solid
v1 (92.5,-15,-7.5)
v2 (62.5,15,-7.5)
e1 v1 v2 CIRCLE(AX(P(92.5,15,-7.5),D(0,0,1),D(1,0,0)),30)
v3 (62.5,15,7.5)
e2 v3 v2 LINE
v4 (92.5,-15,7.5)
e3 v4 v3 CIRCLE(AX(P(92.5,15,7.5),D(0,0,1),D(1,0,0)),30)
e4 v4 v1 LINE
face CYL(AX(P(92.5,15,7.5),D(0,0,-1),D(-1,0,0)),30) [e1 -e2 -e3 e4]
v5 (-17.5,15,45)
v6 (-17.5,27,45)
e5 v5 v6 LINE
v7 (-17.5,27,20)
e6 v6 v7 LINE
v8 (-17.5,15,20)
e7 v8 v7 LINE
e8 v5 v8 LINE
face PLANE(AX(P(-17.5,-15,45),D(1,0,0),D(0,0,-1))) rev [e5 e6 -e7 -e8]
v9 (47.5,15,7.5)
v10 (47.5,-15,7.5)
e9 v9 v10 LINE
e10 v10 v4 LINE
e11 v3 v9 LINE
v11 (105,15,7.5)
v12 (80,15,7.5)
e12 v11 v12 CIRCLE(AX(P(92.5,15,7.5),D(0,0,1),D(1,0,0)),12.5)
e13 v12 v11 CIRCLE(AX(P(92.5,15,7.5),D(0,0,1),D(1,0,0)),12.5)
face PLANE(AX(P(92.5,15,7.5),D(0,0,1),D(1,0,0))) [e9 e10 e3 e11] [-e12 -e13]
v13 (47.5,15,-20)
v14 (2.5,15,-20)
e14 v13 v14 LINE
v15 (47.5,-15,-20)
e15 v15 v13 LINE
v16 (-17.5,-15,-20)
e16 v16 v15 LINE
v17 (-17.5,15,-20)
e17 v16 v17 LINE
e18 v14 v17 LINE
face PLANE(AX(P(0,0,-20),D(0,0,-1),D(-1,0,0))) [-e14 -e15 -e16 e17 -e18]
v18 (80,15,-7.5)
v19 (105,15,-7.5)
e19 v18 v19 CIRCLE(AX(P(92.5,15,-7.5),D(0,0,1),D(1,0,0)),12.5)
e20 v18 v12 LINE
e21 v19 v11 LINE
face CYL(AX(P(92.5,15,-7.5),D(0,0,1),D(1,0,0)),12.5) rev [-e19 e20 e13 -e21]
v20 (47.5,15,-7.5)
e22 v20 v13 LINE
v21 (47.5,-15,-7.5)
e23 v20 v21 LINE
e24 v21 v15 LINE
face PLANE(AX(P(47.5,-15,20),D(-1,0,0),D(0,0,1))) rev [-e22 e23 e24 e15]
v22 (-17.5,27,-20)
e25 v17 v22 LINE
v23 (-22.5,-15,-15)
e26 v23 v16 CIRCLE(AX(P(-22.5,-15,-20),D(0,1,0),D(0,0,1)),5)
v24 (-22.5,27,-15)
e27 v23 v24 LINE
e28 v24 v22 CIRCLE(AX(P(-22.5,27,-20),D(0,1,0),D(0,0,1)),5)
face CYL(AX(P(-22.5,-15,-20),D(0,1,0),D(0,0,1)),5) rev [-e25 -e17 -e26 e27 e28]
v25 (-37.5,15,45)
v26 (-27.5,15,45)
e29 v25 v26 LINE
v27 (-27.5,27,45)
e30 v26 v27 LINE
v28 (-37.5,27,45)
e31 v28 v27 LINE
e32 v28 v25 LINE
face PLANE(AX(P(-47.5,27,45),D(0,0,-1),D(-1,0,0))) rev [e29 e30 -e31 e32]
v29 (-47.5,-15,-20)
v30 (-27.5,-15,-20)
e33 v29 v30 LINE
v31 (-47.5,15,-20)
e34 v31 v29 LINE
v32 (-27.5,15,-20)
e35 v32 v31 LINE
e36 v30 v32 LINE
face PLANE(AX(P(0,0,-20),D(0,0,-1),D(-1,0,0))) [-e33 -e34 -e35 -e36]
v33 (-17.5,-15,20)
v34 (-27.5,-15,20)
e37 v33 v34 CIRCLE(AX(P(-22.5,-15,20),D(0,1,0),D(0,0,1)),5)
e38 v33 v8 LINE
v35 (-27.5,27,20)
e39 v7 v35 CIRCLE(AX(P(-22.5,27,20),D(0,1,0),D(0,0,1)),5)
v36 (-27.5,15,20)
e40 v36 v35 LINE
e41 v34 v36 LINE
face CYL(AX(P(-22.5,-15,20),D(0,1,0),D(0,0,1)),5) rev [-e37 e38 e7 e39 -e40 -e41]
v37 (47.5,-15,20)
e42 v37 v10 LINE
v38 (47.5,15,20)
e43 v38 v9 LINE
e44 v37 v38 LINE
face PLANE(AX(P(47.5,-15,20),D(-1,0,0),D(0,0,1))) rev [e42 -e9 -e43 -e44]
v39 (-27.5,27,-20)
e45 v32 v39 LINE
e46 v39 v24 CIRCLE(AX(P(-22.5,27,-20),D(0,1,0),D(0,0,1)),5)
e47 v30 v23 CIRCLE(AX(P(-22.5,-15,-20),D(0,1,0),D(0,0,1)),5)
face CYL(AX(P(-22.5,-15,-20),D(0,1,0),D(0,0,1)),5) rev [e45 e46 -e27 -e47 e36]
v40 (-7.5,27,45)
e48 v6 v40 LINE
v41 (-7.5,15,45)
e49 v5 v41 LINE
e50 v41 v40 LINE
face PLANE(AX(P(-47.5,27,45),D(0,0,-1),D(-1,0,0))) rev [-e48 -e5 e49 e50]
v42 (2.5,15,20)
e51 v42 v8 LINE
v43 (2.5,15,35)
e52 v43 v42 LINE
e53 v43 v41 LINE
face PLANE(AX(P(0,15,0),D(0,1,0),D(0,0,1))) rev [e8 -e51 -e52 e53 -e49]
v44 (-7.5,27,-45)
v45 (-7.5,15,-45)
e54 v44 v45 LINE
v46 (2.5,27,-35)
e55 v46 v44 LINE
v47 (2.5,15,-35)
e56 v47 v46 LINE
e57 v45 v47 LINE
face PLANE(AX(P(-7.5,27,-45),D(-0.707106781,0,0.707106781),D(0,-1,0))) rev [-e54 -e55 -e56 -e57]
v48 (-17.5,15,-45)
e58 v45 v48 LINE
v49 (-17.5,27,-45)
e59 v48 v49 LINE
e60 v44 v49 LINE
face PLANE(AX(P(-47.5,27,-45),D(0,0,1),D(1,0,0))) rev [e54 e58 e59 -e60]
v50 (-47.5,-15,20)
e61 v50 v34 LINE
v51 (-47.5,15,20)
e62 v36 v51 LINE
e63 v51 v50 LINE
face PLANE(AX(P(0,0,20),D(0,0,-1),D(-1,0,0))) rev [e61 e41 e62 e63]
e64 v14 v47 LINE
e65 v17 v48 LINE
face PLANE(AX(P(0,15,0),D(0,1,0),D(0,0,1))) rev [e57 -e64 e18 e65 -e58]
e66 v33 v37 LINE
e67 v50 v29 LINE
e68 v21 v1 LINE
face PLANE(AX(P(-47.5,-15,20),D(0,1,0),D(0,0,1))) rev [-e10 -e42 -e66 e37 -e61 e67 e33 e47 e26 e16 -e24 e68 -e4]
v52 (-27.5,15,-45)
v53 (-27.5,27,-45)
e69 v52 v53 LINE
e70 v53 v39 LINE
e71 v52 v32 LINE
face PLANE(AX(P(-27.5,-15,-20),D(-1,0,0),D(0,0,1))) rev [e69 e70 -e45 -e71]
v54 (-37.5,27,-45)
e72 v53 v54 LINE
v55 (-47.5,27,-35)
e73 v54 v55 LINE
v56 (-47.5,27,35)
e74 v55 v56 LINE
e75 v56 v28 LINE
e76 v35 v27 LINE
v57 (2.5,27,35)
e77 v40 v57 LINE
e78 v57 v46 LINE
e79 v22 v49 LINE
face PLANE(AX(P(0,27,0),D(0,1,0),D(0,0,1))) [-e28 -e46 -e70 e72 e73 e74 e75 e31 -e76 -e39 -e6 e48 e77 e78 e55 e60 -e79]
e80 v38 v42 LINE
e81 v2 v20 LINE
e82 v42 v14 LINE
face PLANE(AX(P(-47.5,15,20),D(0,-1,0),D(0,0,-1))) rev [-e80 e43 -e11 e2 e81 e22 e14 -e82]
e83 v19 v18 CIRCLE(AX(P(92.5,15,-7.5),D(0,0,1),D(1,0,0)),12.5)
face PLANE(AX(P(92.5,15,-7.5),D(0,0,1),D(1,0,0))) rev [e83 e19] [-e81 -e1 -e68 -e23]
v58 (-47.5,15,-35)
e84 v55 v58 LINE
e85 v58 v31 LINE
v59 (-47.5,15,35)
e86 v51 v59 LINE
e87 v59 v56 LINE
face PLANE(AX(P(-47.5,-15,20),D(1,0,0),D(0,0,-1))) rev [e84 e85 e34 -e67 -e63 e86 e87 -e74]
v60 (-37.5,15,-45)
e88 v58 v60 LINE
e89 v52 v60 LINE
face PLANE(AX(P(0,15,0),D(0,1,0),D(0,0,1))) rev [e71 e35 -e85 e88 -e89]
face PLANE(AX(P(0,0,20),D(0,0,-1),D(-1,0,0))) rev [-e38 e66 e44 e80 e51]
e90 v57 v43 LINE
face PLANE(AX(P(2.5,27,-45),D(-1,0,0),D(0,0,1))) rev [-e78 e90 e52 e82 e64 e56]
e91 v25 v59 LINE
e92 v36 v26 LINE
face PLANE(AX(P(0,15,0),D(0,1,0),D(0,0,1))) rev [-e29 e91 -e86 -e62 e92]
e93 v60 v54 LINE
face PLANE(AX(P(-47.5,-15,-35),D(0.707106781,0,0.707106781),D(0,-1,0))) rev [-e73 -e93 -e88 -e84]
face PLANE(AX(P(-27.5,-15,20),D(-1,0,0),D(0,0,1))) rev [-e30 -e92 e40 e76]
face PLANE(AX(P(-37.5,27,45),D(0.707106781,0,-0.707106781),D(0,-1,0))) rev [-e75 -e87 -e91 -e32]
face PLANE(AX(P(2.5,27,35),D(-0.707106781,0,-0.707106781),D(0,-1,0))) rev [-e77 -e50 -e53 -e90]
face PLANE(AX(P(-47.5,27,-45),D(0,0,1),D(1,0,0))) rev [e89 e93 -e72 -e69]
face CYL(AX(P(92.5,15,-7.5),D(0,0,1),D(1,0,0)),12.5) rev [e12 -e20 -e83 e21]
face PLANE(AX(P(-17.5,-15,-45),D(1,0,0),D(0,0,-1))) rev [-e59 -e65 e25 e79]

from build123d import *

# Parameters (mm, degrees)
ROD_BODY_SKETCH_W                = 95
ROD_BODY_SKETCH_H                = 30
ROD_BODY_30X95_DEPTH             = 20
MOUNTING_PLATE_SKETCH_W          = 50
MOUNTING_PLATE_SKETCH_H          = 90
MOUNTING_PLATE_12MM_DEPTH        = 12
EYE_BOSS_DEPTH                   = 7.5
EYE_HOLE_SKETCH_R                = 12.5
EYE_HOLE_25_DEPTH                = 15
MOUNTING_SLOTS_2X10_DEPTH        = 138.095769446
PLATE_CORNER_CHAMFERS_10X45_SIZE = 10


with BuildPart() as part:
    # Rod Body Sketch → Rod Body 30x95 (new, symmetric)
    with BuildSketch(Plane.XY):
        Rectangle(ROD_BODY_SKETCH_W, ROD_BODY_SKETCH_H)
    extrude(amount=ROD_BODY_30X95_DEPTH, both=True)

    # Mounting Plate Sketch → Mounting Plate 12mm (add)
    with BuildSketch(Plane(origin=(0, 15, 0), x_dir=(1, 0, 0), z_dir=(0, 1, 0))):
        with Locations((-22.5, 0)):
            Rectangle(MOUNTING_PLATE_SKETCH_W, MOUNTING_PLATE_SKETCH_H)
    extrude(amount=MOUNTING_PLATE_12MM_DEPTH)

    # Eye Boss Sketch → Eye Boss (add, symmetric)
    with BuildSketch(Plane.XY):
        with BuildLine():
            Line((92.5, -15), (47.5, -15))
            Line((47.5, -15), (47.5, 15))
            Line((47.5, 15), (62.5, 15))
            ThreePointArc((62.5, 15), (113.713203436, 36.213203436), (92.5, -15))
        make_face()
    extrude(amount=EYE_BOSS_DEPTH, both=True)

    # Eye Hole Sketch → Eye Hole Ø25 (cut)
    with BuildSketch(Plane.XY.offset(7.5)):
        with Locations((92.5, 15)):
            Circle(EYE_HOLE_SKETCH_R)
    extrude(amount=-EYE_HOLE_25_DEPTH, mode=Mode.SUBTRACT)

    # Mounting Slots Sketch → Mounting Slots 2x10 (cut, through all)
    with BuildSketch(Plane(origin=(0, 27, 0), x_dir=(1, 0, 0), z_dir=(0, 1, 0))):
        with BuildLine():
            Line((-27.5, 20), (-27.5, 45))
            Line((-27.5, 45), (-17.5, 45))
            Line((-17.5, 45), (-17.5, 20))
            ThreePointArc((-17.5, 20), (-22.5, 15), (-27.5, 20))
        make_face()
        with BuildLine():
            Line((-27.5, -20), (-27.5, -45))
            Line((-27.5, -45), (-17.5, -45))
            Line((-17.5, -45), (-17.5, -20))
            ThreePointArc((-17.5, -20), (-22.5, -15), (-27.5, -20))
        make_face()
    extrude(amount=-MOUNTING_SLOTS_2X10_DEPTH, mode=Mode.SUBTRACT)

    # Plate Corner Chamfers 10x45
    plate_corner_chamfers_10x45_edges = [part.edges().sort_by_distance(p)[0] for p in [
        (-47.5, 21, -45),
        (-47.5, 21, 45),
        (2.5, 21, 45),
        (2.5, 21, -45),
    ]]
    chamfer(plate_corner_chamfers_10x45_edges, length=PLATE_CORNER_CHAMFERS_10X45_SIZE)


solid = part.part
